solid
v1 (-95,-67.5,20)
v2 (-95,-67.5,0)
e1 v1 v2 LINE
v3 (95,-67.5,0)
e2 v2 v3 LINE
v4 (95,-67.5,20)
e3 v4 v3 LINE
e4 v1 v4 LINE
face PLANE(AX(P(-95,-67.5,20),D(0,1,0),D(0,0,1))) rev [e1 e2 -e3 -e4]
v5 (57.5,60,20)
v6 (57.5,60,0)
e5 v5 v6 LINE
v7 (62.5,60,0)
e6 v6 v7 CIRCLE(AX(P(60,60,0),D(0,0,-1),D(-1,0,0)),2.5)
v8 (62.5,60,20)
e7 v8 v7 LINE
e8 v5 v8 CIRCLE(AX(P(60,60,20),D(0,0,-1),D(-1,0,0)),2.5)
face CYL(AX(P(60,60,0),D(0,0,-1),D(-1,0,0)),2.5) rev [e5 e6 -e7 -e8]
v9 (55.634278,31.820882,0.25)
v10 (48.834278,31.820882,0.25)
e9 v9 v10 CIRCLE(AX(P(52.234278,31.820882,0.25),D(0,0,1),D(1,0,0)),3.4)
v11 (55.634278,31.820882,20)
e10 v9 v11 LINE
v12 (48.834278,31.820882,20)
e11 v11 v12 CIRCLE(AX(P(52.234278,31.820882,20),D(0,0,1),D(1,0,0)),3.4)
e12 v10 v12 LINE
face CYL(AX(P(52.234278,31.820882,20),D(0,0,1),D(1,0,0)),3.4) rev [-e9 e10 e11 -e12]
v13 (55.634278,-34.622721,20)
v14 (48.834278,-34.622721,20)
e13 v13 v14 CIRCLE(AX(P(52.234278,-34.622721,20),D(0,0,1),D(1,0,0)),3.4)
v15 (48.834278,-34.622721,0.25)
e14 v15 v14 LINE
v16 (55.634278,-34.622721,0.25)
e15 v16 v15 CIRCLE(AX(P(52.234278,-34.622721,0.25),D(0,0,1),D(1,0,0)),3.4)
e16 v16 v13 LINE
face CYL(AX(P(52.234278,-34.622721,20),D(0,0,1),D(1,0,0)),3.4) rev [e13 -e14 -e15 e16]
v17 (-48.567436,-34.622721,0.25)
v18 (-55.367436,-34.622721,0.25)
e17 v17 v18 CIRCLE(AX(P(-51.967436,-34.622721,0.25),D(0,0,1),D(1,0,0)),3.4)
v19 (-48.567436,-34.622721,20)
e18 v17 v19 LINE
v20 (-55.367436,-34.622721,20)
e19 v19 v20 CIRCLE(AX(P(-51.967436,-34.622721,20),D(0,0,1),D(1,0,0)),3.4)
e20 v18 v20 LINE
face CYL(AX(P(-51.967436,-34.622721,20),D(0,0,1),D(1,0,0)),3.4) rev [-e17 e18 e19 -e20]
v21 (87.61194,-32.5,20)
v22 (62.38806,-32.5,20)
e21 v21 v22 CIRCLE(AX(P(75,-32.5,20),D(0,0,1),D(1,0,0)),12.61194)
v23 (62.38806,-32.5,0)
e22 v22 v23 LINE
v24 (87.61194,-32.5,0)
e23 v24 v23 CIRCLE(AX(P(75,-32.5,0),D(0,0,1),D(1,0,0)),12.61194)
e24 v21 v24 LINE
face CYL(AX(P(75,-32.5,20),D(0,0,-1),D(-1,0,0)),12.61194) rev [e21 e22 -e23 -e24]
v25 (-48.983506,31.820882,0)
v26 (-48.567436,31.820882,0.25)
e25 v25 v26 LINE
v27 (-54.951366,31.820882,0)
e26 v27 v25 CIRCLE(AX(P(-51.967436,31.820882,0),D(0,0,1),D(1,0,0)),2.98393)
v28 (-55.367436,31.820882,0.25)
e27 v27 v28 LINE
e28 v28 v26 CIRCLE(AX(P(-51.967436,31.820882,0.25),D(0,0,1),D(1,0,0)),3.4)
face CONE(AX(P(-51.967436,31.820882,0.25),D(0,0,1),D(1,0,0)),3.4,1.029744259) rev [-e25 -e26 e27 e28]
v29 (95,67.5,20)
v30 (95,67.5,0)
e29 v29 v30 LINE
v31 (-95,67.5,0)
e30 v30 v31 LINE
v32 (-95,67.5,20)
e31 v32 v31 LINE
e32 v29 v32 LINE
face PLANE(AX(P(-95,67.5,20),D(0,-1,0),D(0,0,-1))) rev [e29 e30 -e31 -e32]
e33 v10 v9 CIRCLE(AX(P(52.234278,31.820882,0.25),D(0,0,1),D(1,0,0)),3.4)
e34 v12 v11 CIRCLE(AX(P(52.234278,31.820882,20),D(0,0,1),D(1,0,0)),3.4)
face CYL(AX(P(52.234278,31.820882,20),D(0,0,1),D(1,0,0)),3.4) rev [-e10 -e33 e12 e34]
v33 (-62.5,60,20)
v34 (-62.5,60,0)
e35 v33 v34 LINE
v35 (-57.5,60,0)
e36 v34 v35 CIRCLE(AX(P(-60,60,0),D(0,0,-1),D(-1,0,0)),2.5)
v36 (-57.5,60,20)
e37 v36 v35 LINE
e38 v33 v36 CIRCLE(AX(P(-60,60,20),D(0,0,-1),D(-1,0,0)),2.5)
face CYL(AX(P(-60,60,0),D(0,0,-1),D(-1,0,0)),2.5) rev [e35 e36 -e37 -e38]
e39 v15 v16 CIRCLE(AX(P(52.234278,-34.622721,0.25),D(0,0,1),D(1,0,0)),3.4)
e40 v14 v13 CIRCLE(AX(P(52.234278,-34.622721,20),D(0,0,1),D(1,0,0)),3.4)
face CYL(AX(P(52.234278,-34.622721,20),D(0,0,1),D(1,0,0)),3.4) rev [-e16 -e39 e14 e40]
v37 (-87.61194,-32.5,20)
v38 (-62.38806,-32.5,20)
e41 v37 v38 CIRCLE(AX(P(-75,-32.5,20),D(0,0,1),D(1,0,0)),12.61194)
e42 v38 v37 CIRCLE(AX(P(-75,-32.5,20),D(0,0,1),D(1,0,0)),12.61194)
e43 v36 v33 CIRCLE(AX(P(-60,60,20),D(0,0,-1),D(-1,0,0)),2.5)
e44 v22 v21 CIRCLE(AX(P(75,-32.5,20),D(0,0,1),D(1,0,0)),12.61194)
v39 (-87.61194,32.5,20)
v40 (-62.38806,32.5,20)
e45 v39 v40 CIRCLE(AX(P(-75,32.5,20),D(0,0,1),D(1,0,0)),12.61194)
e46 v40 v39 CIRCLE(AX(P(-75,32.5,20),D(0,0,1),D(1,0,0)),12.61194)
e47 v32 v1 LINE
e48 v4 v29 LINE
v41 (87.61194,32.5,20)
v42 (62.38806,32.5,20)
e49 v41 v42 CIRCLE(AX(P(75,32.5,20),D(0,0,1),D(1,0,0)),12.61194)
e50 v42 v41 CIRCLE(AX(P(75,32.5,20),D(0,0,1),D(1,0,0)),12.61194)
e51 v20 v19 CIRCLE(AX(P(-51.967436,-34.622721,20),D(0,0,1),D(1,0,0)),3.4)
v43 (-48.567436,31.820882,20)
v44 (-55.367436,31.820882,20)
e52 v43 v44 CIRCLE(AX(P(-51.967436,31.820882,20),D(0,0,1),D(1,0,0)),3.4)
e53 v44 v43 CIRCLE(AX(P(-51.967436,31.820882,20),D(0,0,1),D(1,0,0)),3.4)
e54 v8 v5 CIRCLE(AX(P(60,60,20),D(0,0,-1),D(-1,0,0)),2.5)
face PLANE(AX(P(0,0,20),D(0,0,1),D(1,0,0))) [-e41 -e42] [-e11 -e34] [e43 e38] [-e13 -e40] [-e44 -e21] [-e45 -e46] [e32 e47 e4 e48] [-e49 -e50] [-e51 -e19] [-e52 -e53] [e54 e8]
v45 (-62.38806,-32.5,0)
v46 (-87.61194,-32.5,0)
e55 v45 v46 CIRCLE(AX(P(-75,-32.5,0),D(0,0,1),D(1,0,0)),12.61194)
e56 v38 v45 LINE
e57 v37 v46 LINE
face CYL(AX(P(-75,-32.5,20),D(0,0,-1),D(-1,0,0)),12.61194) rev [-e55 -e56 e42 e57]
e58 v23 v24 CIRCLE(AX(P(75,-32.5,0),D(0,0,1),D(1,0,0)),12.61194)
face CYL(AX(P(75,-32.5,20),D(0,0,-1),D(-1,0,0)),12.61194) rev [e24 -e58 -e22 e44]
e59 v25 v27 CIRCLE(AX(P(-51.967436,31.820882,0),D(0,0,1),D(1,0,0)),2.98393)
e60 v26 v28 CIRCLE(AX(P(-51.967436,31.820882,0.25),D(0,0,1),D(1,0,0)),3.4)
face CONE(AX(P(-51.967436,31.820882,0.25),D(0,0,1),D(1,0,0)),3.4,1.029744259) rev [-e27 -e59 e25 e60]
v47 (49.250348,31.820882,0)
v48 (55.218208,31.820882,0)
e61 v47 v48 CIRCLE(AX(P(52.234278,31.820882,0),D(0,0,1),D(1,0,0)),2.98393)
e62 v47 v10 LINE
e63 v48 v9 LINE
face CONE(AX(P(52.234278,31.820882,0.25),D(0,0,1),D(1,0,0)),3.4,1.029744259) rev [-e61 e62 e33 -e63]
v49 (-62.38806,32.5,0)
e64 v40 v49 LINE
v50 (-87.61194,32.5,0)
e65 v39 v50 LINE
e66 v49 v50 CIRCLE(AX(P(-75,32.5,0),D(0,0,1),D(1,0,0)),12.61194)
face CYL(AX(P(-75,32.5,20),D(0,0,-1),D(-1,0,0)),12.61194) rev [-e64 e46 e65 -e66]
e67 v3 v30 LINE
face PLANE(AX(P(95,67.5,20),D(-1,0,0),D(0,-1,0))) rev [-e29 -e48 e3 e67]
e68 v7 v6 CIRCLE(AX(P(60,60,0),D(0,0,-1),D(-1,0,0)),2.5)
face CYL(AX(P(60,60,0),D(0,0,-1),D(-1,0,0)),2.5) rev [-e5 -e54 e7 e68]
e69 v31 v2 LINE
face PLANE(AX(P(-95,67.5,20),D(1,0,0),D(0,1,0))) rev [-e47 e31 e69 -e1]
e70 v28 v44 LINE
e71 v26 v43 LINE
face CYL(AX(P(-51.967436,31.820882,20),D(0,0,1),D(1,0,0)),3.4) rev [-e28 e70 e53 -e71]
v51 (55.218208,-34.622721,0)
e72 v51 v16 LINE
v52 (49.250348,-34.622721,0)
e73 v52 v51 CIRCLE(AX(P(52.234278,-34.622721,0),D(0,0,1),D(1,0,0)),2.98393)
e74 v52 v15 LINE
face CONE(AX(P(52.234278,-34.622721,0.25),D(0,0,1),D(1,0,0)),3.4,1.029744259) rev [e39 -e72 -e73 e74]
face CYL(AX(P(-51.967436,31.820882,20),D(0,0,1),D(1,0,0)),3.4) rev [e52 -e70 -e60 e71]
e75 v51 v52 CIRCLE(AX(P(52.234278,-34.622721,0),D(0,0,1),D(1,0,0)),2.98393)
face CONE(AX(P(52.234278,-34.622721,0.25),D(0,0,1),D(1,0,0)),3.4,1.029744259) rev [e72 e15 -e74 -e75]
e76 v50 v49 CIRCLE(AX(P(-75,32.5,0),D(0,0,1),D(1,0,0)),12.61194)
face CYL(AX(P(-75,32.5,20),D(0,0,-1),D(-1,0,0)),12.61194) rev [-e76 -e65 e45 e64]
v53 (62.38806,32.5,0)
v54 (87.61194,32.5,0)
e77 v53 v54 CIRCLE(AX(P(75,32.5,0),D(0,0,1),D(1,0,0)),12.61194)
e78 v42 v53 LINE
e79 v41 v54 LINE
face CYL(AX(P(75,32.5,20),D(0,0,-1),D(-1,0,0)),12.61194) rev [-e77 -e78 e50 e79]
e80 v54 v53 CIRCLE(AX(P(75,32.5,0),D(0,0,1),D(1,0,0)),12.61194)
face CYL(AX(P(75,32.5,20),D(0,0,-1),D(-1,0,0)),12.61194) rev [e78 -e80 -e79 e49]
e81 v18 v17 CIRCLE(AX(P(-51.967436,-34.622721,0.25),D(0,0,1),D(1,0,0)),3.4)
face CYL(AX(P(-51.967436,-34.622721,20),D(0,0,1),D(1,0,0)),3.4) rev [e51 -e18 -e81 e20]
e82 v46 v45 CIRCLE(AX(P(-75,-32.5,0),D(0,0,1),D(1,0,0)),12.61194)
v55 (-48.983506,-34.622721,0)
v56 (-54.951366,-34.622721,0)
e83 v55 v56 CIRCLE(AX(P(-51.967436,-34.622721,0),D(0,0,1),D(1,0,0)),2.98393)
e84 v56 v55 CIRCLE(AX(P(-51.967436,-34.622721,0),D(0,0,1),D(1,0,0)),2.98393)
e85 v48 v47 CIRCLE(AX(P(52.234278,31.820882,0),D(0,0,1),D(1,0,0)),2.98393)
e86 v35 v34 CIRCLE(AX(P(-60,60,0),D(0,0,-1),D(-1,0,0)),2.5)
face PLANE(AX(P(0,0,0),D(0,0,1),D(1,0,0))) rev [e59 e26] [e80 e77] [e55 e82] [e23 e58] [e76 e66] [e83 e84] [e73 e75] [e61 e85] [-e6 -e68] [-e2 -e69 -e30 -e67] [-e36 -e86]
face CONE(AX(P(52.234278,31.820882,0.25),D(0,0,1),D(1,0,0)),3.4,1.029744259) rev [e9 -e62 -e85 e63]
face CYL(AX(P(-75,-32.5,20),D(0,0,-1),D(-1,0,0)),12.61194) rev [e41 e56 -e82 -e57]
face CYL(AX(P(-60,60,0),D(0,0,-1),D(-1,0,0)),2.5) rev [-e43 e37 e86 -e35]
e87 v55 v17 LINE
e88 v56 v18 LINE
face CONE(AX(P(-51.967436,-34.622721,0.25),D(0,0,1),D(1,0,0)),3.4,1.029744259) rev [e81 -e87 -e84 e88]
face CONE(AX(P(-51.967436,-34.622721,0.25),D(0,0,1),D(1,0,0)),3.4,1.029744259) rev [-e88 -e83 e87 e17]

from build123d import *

# Parameters (mm, degrees)
SKETCH1_W             = 190
SKETCH1_H             = 135
SKETCH1_R             = 12.611940299
BOSS_EXTRUDE1_DEPTH   = 20
M6_TAPPED_HOLE6_D     = 5
M8_TAPPED_HOLE1_D     = 6.8
M8_TAPPED_HOLE1_DEPTH = 19.75
M8_TAPPED_HOLE1_TIP   = 2.042926105


with BuildPart() as part:
    # Sketch1 → Boss-Extrude1 (new body)
    with BuildSketch(Plane.XY):
        Rectangle(SKETCH1_W, SKETCH1_H)
        with Locations((-75, 32.5)):
            Circle(SKETCH1_R, mode=Mode.SUBTRACT)
        with Locations((-75, -32.5)):
            Circle(SKETCH1_R, mode=Mode.SUBTRACT)
        with Locations((75, 32.5)):
            Circle(SKETCH1_R, mode=Mode.SUBTRACT)
        with Locations((75, -32.5)):
            Circle(SKETCH1_R, mode=Mode.SUBTRACT)
    extrude(amount=BOSS_EXTRUDE1_DEPTH)

    # M6 Tapped Hole6 (through all)
    with Locations(Plane(origin=(0, 0, 0), x_dir=(-1, 0, 0), z_dir=(0, 0, -1))):
        with Locations((-60, 60), (60, 60)):
            Hole(M6_TAPPED_HOLE6_D / 2)

    # M8 Tapped Hole1
    with Locations(Plane.XY.offset(20)):
        with Locations((-51.96743603, 31.820881882), (-51.96743603, -34.622720538), (52.234277806, -34.622720538), (52.234277806, 31.820881882)):
            Hole(M8_TAPPED_HOLE1_D / 2, depth=M8_TAPPED_HOLE1_DEPTH)
            with Locations((0, 0, -(M8_TAPPED_HOLE1_DEPTH + M8_TAPPED_HOLE1_TIP / 2))):  # 118° drill point
                Cone(0, M8_TAPPED_HOLE1_D / 2, M8_TAPPED_HOLE1_TIP, mode=Mode.SUBTRACT)


solid = part.part
